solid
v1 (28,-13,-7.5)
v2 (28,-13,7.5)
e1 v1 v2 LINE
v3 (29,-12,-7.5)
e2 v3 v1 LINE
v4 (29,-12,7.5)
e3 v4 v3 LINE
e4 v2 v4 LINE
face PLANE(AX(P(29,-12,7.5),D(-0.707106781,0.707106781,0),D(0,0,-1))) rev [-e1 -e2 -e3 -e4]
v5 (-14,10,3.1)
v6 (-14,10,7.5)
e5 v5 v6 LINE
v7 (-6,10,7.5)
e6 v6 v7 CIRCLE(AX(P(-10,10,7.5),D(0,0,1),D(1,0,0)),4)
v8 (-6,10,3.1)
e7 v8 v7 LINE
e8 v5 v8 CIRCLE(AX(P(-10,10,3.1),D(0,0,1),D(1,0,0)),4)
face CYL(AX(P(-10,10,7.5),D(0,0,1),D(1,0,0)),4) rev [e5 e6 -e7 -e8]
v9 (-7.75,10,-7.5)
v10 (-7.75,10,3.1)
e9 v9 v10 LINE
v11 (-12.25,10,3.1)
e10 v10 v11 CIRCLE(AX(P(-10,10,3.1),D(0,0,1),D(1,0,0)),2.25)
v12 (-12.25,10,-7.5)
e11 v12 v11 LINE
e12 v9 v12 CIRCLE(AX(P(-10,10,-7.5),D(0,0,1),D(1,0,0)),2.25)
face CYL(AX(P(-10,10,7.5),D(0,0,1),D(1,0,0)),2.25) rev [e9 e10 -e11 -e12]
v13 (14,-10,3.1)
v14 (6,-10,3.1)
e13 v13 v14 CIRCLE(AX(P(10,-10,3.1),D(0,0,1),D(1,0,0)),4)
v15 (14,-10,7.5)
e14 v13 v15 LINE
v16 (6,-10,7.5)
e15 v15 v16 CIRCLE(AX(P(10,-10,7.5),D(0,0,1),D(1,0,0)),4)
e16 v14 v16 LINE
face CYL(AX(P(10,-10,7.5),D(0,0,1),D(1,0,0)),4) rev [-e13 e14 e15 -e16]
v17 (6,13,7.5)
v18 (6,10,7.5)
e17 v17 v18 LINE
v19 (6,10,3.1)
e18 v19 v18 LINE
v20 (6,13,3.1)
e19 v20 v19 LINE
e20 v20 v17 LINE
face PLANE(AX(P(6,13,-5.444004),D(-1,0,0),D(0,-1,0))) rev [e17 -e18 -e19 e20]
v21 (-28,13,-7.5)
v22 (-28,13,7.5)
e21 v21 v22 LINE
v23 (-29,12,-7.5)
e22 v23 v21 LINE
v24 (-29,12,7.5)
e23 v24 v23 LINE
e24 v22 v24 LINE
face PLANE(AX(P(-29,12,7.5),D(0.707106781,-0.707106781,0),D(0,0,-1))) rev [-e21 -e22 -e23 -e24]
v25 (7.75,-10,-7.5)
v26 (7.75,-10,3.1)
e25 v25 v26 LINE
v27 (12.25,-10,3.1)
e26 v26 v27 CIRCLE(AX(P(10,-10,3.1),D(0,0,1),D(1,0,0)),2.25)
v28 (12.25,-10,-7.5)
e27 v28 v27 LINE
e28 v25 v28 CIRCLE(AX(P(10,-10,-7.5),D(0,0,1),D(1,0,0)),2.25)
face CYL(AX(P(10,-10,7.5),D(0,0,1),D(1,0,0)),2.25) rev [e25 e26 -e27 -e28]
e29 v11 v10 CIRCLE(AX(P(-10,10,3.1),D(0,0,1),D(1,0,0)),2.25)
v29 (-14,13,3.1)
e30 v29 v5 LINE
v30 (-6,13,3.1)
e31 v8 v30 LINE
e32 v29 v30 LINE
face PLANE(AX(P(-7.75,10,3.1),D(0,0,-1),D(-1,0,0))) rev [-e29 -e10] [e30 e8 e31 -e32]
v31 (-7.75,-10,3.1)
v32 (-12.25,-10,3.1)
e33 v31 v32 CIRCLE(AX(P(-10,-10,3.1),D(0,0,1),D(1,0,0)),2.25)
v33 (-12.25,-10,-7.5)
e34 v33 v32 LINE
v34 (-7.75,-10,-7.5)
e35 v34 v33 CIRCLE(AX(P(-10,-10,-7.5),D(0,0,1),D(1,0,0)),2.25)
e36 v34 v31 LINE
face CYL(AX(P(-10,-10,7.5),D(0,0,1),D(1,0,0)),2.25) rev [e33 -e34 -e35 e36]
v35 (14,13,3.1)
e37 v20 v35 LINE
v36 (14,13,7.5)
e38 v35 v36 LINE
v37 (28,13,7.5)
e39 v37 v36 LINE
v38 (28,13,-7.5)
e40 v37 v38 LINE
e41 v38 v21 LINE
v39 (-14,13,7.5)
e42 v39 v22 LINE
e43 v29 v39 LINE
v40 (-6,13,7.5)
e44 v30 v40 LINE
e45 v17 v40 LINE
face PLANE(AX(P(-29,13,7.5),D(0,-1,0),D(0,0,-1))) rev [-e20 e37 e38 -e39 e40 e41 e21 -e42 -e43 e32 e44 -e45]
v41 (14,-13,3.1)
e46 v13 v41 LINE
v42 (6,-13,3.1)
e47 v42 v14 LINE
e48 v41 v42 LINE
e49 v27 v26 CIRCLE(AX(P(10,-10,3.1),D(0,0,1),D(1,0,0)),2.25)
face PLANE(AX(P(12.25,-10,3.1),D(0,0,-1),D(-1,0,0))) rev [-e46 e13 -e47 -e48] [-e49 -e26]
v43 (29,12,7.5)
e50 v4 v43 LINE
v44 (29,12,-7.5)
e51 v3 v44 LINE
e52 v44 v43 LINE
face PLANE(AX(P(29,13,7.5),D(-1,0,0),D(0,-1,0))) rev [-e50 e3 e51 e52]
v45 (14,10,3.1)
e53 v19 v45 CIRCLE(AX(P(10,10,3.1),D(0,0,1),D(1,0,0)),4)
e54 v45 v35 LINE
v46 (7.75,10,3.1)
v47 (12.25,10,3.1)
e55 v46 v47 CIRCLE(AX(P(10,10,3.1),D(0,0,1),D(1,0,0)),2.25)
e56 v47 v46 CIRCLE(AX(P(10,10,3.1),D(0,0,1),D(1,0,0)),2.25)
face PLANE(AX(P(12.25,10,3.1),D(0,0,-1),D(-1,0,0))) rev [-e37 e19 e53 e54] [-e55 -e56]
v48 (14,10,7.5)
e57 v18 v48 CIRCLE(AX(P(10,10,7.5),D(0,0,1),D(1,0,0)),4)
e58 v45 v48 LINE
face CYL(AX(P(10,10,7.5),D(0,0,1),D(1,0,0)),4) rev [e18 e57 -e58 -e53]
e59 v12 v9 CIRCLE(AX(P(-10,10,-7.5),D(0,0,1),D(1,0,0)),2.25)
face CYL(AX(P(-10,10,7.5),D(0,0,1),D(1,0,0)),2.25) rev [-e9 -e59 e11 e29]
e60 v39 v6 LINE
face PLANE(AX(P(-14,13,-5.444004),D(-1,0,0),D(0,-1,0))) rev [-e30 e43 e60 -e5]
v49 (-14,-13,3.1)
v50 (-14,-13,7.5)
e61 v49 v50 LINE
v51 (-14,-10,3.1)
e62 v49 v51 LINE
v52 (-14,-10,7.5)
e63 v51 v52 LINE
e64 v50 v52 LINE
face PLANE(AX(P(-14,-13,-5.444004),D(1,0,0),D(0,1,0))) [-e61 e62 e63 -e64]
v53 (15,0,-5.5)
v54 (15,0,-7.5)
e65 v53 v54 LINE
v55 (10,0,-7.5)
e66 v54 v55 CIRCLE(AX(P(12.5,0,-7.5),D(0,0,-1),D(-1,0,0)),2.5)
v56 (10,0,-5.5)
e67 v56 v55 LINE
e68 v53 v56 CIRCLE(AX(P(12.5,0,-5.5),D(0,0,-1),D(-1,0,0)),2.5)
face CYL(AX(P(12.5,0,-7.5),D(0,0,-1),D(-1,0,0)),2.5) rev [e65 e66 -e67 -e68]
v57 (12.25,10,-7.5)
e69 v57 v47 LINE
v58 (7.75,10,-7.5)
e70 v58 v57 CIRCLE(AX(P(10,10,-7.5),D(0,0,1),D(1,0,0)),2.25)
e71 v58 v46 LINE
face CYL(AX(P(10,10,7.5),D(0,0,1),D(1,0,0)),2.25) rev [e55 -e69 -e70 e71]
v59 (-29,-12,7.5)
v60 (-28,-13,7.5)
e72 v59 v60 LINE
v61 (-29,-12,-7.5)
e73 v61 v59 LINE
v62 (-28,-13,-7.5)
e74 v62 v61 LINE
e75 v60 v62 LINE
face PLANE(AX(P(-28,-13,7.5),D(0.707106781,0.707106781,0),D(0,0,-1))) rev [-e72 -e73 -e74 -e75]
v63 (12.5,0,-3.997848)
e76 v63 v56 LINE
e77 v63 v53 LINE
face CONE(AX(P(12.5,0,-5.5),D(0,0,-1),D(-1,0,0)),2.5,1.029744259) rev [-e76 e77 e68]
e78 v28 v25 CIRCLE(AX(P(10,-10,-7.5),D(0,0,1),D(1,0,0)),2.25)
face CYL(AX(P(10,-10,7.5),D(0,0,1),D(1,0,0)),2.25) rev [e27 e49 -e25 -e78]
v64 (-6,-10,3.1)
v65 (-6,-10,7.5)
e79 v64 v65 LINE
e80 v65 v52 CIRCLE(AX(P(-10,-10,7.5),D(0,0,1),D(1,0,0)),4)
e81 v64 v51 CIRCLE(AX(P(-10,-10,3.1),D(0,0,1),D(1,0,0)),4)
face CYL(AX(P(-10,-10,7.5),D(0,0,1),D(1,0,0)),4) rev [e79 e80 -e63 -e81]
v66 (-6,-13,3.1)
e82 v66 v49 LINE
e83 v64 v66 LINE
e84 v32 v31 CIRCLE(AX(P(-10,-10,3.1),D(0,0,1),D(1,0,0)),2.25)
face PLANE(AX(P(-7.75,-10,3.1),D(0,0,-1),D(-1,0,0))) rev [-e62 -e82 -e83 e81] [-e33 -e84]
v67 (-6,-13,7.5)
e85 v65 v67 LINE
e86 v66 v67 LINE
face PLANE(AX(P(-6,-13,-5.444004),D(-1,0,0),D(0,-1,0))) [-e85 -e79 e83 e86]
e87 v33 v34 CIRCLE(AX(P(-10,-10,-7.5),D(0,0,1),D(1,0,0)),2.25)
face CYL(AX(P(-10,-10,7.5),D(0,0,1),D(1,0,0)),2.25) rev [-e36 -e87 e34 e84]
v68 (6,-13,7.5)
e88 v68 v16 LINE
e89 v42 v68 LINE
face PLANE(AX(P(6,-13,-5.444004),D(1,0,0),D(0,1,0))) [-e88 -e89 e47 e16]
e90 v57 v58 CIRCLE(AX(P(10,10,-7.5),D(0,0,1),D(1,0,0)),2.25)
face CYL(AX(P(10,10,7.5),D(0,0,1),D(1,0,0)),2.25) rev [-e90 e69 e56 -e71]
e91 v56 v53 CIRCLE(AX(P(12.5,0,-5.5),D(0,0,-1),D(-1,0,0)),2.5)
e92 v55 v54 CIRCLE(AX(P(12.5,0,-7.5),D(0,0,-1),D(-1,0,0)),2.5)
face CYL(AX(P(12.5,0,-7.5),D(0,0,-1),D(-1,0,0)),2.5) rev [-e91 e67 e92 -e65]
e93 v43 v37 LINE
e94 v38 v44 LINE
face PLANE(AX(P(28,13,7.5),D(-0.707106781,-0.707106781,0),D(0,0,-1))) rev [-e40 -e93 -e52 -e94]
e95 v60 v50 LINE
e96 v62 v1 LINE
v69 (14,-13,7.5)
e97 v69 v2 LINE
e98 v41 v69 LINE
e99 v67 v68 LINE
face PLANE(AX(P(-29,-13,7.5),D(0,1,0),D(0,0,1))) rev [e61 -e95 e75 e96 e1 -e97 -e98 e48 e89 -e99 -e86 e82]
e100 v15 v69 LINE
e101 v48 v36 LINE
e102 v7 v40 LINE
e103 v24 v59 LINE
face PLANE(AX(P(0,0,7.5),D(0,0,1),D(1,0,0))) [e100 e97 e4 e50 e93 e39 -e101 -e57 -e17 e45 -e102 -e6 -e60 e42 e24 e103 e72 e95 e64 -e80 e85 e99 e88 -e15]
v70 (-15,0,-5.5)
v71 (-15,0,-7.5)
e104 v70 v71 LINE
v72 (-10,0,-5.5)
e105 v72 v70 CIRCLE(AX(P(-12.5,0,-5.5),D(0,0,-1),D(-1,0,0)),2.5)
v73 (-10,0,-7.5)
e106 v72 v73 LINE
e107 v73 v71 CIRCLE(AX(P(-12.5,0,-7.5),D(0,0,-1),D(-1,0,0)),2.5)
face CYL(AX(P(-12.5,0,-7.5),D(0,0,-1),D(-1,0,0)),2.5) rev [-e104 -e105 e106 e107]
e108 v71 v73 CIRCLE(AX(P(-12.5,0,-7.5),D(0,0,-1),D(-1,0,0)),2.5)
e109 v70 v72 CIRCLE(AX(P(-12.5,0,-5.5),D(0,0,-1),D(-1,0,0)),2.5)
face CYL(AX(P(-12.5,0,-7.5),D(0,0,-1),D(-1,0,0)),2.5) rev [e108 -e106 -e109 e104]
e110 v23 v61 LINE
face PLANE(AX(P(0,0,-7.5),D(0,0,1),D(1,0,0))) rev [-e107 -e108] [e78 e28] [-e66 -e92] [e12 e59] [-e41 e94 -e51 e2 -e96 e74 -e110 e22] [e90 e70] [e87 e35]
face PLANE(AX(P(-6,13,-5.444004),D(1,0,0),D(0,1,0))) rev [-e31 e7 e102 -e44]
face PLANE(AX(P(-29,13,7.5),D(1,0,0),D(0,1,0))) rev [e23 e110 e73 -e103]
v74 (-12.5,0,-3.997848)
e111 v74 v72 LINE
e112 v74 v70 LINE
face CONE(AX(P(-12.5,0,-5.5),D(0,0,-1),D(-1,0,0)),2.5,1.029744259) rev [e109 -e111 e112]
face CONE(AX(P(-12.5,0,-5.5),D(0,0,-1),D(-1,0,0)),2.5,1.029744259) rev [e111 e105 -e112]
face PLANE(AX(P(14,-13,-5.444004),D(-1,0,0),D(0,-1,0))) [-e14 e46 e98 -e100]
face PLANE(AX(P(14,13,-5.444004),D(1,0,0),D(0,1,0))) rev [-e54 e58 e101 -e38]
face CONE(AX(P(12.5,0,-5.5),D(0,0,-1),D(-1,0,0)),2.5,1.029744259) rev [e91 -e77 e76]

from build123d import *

# Parameters (mm, degrees)
SKETCH1_W                                           = 58
SKETCH1_H                                           = 26
BOSS_EXTRUDE1_DEPTH                                 = 7.5
CBORE_FOR_M4_HEX_SOCKET_HEAD_CAP_SCREW1_D           = 4.5
CBORE_FOR_M4_HEX_SOCKET_HEAD_CAP_SCREW1_CBORE_D     = 8
CBORE_FOR_M4_HEX_SOCKET_HEAD_CAP_SCREW1_CBORE_DEPTH = 4.4
SKETCH6_W                                           = 8
SKETCH6_H                                           = 3
CUT_EXTRUDE1_DEPTH                                  = 4.4
BLIND_PIN_HOLE1_SIZE_MM_D                           = 5
BLIND_PIN_HOLE1_SIZE_MM_DEPTH                       = 2
BLIND_PIN_HOLE1_SIZE_MM_TIP                         = 1.502151548
CHAMFER1_SIZE                                       = 1


with BuildPart() as part:
    # Sketch1 → Boss-Extrude1 (new, symmetric)
    with BuildSketch(Plane.XY):
        Rectangle(SKETCH1_W, SKETCH1_H)
    extrude(amount=BOSS_EXTRUDE1_DEPTH, both=True)

    # CBORE for M4 Hex Socket Head Cap Screw1 (through all)
    with Locations(Plane.XY.offset(7.5)):
        with Locations((-10, 10), (-10, -10), (10, -10), (10, 10)):
            CounterBoreHole(CBORE_FOR_M4_HEX_SOCKET_HEAD_CAP_SCREW1_D / 2, CBORE_FOR_M4_HEX_SOCKET_HEAD_CAP_SCREW1_CBORE_D / 2, CBORE_FOR_M4_HEX_SOCKET_HEAD_CAP_SCREW1_CBORE_DEPTH)

    # Sketch6 → Cut-Extrude1 (cut)
    with BuildSketch(Plane.XY.offset(7.5)):
        with Locations((-10, 11.5)):
            Rectangle(SKETCH6_W, SKETCH6_H)
        with Locations((10, 11.5)):
            Rectangle(SKETCH6_W, SKETCH6_H)
    cut_extrude1 = extrude(amount=-CUT_EXTRUDE1_DEPTH, mode=Mode.SUBTRACT)

    # Mirror1: Cut-Extrude1 across plane
    add(cut_extrude1.mirror(Plane.ZX), mode=Mode.SUBTRACT)

    # Blind Pin Hole1 (size mm)
    with Locations(Plane(origin=(0, 0, -7.5), x_dir=(-1, 0, 0), z_dir=(0, 0, -1))):
        with Locations((-12.5, 0), (12.5, 0)):
            Hole(BLIND_PIN_HOLE1_SIZE_MM_D / 2, depth=BLIND_PIN_HOLE1_SIZE_MM_DEPTH)
            with Locations((0, 0, -(BLIND_PIN_HOLE1_SIZE_MM_DEPTH + BLIND_PIN_HOLE1_SIZE_MM_TIP / 2))):  # 118° drill point
                Cone(0, BLIND_PIN_HOLE1_SIZE_MM_D / 2, BLIND_PIN_HOLE1_SIZE_MM_TIP, mode=Mode.SUBTRACT)

    # Chamfer1
    chamfer1_edges = [part.edges().sort_by_distance(p)[0] for p in [
        (29, -13, 0),
        (-29, -13, 0),
        (-29, 13, 0),
        (29, 13, 0),
    ]]
    chamfer(chamfer1_edges, length=CHAMFER1_SIZE)


solid = part.part
